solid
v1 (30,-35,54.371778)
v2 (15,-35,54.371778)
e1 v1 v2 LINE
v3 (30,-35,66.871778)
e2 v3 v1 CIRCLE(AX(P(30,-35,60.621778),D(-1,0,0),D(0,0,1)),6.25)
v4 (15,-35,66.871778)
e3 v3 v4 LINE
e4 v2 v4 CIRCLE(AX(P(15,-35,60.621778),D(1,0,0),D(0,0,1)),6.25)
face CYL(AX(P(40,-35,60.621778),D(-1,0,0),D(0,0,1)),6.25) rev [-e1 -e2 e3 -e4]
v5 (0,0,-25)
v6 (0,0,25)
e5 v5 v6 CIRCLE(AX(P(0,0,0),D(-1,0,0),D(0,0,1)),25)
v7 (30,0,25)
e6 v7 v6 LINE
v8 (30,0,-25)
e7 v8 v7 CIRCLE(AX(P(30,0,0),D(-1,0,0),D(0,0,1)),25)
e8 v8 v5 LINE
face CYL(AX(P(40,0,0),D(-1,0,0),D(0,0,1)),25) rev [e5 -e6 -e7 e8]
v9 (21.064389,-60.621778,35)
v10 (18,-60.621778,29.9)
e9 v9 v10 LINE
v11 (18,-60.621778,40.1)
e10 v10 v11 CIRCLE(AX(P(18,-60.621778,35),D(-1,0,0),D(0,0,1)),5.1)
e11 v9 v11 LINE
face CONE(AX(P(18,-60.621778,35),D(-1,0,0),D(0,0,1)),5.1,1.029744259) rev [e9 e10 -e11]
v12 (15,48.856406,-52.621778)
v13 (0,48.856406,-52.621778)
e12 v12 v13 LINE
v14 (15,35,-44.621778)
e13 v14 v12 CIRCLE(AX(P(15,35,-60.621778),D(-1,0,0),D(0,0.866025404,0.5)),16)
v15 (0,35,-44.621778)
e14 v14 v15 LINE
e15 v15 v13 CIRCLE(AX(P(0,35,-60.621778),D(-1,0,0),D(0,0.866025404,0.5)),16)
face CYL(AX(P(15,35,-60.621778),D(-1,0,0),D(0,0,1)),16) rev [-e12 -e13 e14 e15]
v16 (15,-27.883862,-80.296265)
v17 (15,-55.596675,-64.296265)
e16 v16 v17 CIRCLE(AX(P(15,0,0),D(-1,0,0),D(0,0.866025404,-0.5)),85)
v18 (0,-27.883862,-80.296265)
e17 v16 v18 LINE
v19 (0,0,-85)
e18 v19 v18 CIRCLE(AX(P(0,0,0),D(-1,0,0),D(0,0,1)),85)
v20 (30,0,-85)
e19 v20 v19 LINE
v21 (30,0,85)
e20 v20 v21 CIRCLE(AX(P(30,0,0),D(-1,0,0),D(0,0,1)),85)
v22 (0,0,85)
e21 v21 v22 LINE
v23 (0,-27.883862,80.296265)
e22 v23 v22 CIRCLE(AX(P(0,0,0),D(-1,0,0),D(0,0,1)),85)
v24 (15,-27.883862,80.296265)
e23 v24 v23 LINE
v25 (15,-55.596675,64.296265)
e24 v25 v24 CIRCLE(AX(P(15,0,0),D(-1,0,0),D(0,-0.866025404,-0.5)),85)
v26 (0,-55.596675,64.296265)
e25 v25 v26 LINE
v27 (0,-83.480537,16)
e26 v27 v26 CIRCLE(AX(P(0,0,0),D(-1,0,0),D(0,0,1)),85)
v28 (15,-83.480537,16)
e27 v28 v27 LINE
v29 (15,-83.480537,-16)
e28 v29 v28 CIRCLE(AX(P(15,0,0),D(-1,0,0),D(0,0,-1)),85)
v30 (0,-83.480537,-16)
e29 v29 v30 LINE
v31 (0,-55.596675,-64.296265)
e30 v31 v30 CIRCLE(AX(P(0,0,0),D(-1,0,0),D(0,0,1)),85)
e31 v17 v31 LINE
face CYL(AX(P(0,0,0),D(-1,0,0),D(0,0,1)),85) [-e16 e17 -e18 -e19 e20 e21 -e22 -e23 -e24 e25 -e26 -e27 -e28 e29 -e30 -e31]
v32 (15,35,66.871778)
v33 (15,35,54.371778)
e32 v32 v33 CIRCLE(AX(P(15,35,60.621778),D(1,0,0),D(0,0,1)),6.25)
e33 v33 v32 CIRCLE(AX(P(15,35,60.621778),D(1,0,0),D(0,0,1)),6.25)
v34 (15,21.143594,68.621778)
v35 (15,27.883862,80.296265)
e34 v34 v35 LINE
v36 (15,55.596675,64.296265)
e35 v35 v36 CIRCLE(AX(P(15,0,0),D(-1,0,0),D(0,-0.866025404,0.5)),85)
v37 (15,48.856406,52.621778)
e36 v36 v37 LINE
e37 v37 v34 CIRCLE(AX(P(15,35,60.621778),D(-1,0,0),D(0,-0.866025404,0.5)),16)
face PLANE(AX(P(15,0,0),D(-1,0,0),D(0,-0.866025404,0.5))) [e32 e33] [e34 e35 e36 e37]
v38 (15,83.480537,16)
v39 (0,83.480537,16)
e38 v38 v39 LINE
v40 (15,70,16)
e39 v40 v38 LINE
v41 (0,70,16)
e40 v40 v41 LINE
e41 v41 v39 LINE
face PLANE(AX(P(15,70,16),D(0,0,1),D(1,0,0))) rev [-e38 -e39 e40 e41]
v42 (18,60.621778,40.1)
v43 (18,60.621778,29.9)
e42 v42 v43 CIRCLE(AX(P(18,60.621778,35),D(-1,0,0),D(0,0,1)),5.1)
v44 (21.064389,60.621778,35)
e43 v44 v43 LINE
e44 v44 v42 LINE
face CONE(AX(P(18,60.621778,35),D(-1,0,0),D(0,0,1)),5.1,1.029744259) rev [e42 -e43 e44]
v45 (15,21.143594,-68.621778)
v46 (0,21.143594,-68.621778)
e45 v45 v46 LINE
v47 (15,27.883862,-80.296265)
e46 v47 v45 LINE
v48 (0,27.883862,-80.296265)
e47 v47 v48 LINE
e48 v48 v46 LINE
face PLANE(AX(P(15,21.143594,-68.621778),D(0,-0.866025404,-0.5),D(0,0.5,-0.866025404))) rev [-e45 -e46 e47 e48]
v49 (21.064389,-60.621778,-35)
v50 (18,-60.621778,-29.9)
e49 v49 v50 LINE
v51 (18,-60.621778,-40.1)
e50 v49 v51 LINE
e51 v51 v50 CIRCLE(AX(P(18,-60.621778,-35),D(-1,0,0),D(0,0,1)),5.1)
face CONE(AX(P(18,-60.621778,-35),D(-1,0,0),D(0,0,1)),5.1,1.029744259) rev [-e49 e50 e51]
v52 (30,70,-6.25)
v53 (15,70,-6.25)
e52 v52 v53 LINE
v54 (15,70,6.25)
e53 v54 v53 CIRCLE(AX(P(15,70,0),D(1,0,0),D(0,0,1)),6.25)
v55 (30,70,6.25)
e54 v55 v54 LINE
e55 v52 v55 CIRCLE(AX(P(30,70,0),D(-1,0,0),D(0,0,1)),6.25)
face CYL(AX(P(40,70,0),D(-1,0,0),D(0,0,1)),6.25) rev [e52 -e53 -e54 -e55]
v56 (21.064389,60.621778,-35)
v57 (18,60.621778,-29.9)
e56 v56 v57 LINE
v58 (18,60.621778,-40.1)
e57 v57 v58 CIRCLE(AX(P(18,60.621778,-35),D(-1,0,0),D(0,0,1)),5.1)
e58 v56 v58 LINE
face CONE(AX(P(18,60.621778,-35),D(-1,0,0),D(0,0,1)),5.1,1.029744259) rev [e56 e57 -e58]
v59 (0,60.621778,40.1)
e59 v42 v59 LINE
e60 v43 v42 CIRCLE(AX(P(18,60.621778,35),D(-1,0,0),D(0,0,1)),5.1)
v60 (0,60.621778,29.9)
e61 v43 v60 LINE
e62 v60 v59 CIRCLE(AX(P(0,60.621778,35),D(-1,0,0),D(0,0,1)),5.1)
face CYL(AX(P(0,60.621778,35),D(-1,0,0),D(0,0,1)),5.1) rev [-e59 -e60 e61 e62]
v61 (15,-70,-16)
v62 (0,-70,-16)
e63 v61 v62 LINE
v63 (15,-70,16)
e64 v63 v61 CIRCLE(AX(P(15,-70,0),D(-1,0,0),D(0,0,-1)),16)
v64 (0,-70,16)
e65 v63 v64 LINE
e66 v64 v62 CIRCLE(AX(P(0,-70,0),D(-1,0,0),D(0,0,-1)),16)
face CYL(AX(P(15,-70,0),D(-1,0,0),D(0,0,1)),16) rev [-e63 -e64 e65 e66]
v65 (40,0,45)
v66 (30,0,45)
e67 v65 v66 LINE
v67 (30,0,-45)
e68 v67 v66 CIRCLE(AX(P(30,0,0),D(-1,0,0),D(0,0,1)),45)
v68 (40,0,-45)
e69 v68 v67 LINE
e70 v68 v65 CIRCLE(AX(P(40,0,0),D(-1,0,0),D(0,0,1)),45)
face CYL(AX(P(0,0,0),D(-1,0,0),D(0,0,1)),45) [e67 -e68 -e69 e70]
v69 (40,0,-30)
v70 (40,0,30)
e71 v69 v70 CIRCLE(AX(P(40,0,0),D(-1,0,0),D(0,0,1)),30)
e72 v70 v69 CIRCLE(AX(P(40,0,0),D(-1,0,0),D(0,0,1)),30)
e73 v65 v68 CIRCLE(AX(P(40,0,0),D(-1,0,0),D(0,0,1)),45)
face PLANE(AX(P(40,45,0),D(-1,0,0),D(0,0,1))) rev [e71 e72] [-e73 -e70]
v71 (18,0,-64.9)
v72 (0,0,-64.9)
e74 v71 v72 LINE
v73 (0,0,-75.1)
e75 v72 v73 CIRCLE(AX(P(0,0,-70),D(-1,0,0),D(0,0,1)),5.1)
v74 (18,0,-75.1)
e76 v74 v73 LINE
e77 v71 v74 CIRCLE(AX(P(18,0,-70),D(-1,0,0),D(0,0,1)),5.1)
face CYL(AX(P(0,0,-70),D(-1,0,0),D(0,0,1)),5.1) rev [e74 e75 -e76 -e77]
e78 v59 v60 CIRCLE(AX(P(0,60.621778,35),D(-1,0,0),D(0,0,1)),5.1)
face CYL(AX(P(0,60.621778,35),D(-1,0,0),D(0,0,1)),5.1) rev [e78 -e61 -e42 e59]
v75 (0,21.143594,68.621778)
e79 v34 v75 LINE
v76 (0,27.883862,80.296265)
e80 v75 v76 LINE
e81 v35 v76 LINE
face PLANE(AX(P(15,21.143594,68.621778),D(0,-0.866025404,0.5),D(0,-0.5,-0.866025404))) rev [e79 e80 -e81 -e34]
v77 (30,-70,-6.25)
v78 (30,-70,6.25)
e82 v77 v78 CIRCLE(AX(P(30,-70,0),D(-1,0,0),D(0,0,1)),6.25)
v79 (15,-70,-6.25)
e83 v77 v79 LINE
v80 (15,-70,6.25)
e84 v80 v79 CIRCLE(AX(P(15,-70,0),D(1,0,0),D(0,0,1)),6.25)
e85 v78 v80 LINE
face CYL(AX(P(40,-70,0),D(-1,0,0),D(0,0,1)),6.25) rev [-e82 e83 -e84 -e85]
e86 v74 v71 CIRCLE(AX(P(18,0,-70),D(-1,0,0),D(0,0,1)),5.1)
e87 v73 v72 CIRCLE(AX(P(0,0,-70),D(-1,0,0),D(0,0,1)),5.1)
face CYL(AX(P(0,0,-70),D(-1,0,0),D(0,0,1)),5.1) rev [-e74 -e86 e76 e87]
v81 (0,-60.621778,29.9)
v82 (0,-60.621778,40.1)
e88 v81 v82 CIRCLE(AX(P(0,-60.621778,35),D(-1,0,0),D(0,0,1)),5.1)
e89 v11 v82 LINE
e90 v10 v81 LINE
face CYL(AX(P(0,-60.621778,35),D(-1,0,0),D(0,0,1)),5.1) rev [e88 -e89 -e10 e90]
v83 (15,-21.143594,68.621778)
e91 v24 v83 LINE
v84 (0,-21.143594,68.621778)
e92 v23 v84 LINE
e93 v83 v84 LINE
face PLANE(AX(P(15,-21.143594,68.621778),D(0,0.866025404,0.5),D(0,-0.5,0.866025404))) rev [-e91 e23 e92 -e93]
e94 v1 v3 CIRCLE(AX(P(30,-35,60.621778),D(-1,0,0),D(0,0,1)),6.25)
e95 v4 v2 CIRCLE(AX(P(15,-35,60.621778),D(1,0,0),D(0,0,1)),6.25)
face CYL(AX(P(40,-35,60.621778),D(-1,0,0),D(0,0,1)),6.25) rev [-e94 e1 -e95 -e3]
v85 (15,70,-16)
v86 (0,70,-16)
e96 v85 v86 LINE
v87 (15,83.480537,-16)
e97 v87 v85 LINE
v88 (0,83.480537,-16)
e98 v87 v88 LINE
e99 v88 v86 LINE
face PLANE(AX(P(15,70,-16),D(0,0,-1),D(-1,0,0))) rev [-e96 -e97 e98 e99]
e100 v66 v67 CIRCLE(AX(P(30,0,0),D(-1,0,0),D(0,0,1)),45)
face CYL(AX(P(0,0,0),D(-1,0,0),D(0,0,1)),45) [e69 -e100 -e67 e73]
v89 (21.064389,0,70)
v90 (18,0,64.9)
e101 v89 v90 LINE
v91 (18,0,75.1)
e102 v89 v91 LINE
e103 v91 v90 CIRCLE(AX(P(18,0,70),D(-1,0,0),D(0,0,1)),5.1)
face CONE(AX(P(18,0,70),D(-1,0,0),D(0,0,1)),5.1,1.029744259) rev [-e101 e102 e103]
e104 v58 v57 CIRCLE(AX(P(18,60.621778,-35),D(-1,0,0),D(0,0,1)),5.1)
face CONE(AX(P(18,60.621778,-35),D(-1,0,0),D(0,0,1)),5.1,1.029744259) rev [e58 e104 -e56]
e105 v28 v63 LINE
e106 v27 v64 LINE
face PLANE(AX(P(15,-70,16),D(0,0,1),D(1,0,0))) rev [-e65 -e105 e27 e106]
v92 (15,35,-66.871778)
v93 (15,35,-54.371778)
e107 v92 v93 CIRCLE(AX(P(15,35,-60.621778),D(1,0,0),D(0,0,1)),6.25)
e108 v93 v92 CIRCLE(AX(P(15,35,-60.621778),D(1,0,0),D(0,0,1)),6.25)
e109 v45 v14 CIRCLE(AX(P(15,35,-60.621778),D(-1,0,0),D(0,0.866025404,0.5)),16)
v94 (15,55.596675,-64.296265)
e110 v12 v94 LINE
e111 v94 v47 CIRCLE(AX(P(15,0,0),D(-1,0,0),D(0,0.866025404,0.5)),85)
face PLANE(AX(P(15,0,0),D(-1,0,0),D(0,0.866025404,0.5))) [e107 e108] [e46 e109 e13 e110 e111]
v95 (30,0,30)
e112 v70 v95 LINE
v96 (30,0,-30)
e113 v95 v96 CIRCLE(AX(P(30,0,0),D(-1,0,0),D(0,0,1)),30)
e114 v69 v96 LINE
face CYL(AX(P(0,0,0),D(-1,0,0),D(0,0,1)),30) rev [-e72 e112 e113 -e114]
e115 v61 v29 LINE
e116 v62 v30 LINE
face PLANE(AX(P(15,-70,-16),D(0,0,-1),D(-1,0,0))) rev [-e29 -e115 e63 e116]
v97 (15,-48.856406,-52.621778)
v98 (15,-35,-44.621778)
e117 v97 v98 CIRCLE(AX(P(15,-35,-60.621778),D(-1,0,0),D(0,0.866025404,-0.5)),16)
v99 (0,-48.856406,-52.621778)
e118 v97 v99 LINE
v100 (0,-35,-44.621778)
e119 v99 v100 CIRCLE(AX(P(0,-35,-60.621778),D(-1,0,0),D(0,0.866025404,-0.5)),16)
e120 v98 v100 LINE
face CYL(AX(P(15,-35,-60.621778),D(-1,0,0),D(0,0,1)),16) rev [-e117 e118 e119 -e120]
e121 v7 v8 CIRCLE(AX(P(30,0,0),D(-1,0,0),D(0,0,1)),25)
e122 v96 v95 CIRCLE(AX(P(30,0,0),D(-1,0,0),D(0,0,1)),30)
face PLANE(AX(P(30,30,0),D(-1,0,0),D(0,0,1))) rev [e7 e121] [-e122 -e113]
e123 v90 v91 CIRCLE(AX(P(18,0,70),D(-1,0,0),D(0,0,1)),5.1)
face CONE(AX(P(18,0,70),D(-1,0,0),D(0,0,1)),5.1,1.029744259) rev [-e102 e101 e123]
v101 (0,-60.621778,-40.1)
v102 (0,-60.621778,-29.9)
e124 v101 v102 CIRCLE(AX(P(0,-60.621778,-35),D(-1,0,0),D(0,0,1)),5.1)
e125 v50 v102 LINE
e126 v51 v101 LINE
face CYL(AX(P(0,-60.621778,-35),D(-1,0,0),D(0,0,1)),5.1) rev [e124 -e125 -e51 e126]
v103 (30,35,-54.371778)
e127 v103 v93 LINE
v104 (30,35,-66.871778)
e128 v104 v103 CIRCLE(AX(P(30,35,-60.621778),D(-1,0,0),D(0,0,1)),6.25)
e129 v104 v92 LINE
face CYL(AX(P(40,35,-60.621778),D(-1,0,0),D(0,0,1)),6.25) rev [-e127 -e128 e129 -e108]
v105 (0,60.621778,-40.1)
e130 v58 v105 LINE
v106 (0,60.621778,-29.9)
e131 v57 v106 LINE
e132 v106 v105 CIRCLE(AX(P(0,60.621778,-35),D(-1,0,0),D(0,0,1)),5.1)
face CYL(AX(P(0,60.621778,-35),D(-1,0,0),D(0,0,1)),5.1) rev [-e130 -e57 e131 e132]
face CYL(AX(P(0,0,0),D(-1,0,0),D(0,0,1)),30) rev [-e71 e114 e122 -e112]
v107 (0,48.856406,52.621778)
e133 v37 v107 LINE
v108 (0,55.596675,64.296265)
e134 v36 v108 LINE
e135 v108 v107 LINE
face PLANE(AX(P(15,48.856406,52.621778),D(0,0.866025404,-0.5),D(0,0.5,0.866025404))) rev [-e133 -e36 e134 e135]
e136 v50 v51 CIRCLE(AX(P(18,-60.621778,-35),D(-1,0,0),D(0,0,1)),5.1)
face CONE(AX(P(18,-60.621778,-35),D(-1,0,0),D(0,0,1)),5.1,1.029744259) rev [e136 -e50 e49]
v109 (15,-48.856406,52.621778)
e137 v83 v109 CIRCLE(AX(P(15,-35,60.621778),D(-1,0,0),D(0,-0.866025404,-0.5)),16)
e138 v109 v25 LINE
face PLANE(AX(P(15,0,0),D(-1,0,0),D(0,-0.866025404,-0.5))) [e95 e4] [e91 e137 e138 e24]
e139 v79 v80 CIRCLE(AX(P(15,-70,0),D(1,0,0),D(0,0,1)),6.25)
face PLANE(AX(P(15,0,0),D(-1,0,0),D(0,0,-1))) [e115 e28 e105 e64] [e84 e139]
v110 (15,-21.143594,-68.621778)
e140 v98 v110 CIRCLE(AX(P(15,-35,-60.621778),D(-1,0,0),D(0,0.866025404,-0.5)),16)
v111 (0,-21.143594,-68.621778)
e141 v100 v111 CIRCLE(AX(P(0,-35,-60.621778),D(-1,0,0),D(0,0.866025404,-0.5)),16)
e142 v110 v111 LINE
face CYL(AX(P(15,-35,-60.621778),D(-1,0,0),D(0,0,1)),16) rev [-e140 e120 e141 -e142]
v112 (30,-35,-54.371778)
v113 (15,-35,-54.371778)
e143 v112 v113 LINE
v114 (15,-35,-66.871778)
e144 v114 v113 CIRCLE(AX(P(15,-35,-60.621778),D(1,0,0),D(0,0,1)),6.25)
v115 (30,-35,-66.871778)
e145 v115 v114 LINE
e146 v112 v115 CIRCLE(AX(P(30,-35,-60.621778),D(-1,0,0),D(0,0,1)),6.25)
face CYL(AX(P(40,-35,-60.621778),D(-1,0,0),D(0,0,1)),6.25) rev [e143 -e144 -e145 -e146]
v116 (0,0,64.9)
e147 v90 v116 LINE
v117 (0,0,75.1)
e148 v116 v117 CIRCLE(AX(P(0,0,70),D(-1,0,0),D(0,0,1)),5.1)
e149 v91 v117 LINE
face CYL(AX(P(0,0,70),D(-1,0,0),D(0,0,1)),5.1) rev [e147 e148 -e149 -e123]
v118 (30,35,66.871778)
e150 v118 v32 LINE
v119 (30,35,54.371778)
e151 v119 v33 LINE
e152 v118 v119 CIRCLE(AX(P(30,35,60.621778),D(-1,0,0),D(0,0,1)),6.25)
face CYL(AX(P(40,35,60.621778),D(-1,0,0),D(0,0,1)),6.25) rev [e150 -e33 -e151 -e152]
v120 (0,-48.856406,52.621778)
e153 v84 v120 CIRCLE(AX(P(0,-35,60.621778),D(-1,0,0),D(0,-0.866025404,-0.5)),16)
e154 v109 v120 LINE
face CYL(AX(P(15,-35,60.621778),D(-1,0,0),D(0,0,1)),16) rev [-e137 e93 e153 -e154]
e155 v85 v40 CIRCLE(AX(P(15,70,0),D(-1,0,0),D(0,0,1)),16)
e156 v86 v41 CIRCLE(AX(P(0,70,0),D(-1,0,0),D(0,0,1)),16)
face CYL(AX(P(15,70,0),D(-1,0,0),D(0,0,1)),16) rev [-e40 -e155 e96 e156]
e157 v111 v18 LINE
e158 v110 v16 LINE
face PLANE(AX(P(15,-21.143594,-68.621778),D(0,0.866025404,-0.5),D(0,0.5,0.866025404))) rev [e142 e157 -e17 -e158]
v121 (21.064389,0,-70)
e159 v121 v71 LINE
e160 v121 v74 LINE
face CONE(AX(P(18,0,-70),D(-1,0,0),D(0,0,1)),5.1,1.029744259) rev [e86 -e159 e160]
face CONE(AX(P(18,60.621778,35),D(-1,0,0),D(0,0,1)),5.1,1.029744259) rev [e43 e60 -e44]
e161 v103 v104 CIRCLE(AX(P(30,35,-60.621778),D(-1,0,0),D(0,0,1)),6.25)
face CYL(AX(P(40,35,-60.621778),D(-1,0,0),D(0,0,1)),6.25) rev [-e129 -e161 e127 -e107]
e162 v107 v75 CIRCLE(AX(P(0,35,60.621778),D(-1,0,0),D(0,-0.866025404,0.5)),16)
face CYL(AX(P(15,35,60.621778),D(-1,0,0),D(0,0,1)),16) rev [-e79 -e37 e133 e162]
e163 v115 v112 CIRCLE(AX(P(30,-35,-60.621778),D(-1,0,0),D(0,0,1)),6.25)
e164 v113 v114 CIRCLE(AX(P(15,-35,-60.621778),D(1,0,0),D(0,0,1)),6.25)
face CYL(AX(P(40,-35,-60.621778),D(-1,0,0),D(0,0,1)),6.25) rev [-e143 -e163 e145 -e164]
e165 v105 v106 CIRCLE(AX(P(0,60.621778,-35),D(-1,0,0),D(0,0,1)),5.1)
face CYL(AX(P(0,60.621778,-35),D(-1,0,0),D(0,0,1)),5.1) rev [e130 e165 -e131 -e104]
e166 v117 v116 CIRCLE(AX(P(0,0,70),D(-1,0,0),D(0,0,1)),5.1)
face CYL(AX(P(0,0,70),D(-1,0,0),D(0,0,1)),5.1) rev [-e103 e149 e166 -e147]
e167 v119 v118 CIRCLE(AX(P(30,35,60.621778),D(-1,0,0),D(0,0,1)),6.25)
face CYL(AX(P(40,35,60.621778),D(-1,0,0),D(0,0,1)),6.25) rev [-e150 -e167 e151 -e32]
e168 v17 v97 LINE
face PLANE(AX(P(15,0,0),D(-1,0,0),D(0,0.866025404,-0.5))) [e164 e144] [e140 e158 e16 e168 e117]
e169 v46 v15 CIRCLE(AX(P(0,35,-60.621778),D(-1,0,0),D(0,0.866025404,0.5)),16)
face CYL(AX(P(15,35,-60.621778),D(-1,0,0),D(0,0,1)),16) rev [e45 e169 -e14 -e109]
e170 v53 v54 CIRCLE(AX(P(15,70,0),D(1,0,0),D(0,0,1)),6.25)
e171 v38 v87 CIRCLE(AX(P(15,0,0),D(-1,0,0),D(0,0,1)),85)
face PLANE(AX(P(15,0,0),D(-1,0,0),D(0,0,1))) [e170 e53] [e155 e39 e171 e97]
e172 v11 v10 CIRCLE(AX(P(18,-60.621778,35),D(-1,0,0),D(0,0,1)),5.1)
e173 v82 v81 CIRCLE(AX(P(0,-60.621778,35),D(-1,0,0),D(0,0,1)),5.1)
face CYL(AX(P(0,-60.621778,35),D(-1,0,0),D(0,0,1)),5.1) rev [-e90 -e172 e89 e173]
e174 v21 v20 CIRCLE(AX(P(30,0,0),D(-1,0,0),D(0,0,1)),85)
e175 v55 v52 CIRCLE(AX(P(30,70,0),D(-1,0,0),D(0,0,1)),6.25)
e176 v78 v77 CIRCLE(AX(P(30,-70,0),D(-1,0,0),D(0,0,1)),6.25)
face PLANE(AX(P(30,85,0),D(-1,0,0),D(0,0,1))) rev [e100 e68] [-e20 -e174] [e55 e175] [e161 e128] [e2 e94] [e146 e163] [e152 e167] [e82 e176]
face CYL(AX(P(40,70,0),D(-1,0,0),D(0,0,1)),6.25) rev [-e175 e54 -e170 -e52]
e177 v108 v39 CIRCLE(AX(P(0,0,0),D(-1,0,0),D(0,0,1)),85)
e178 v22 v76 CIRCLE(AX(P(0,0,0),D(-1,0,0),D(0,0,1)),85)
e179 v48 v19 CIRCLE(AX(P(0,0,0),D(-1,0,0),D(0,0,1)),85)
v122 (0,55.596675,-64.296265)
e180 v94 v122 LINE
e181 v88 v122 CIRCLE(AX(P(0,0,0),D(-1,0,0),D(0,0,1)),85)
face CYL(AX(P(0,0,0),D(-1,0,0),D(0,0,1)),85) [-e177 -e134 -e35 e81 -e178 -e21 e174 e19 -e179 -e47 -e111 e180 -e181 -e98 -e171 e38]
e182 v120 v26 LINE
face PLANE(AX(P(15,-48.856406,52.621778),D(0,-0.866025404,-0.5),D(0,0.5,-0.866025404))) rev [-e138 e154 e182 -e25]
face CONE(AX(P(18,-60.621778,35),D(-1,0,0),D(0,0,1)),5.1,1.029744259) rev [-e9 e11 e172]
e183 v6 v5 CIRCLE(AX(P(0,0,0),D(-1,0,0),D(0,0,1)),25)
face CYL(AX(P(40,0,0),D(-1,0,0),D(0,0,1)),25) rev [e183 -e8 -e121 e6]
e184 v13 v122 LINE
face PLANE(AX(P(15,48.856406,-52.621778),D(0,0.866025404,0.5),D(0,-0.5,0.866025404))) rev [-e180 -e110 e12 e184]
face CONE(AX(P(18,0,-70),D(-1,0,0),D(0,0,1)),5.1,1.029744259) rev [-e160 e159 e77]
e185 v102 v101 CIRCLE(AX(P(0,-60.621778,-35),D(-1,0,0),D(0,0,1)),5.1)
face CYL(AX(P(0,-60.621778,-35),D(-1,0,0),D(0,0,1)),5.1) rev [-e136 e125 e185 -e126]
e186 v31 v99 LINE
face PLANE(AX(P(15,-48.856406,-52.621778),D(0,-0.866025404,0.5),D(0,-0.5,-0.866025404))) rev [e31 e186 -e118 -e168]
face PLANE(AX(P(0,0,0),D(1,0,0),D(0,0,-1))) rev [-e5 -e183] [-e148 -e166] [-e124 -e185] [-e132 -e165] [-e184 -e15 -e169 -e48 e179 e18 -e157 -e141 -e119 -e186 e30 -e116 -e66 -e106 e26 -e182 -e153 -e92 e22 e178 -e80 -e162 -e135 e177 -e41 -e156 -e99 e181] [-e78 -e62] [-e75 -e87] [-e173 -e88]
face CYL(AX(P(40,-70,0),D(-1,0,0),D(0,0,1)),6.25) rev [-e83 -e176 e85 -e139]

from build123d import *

# Parameters (mm, degrees)
SKETCH_2_R               = 6.25
CUT_EXTRUDE_1_DEPTH      = 127.688594593
PATTERN_CIRCULAR_1_COUNT = 6
SKETCH_3_R               = 25
CUT_EXTRUDE_2_DEPTH      = 127.688594593
CUT_EXTRUDE_START        = -15
CUT_EXTRUDE_3_DEPTH      = 15
PATTERN_CIRCULAR_2_COUNT = 6
PATTERN_CIRCULAR_3_COUNT = 6


with BuildPart() as part:
    # 草图1 → 旋转1 (revolve)
    with BuildSketch(Plane.XY, mode=Mode.PRIVATE) as revolve_1_sk:
        Polygon((0, 0), (0, 85), (30, 85), (30, 45), (40, 45), (40, 30), (30, 30), (30, 0), align=None)
    revolve(revolve_1_sk.sketch.rotate(Axis((0, 0, 0), (1, 0, 0)), 90), axis=Axis((0, 0, 0), (1, 0, 0)))

    # 草图2 → 切除-拉伸1 (cut, through all)
    with BuildSketch(Plane.ZY):
        with Locations((0, 70)):
            Circle(SKETCH_2_R)
    cut_extrude_1 = extrude(amount=-CUT_EXTRUDE_1_DEPTH, mode=Mode.SUBTRACT)

    # 阵列(圆周)1: 切除-拉伸1 ×6 about axis
    pattern_circular_1_axis = Axis((0, 0, 0), (1, 0, 0))
    for i in range(1, PATTERN_CIRCULAR_1_COUNT):
        add(cut_extrude_1.rotate(pattern_circular_1_axis, i * 360 / PATTERN_CIRCULAR_1_COUNT), mode=Mode.SUBTRACT)

    # 草图3 → 切除-拉伸2 (cut, through all)
    with BuildSketch(Plane.ZY):
        Circle(SKETCH_3_R)
    extrude(amount=-CUT_EXTRUDE_2_DEPTH, mode=Mode.SUBTRACT)

    # 草图6 → 切除-拉伸3 (cut)
    with BuildSketch(Plane.ZY.offset(CUT_EXTRUDE_START)):
        with BuildLine():
            Line((-16, 70), (-16, 83.480536654))
            ThreePointArc((-16, 83.480536654), (0, 85), (16, 83.480536654))
            Line((16, 83.480536654), (16, 70))
            ThreePointArc((16, 70), (0, 54), (-16, 70))
        make_face()
    cut_extrude_3 = extrude(amount=CUT_EXTRUDE_3_DEPTH, mode=Mode.SUBTRACT)

    # 阵列(圆周)2: 切除-拉伸3 ×6 about axis
    pattern_circular_2_axis = Axis((0, 0, 0), (1, 0, 0))
    for i in range(1, PATTERN_CIRCULAR_2_COUNT):
        add(cut_extrude_3.rotate(pattern_circular_2_axis, i * 360 / PATTERN_CIRCULAR_2_COUNT), mode=Mode.SUBTRACT)

    # 草图8 → M12 螺纹孔1 (revolve, cut)
    with BuildSketch(Plane(origin=(0, 60.621778265, 35), x_dir=(0, 0, 1), z_dir=(0, 1, 0))):
        Polygon((0, 0), (0, 21.064389157), (5.1, 18), (5.1, 0), align=None)
    hole_wizard_m12_1 = revolve(axis=Axis((-6.35, 60.621778265, 35), (1, 0, 0)), mode=Mode.SUBTRACT)

    # 阵列(圆周)3: M12 螺纹孔1 ×6 about axis
    pattern_circular_3_axis = Axis((0, 0, 0), (1, 0, 0))
    for i in range(1, PATTERN_CIRCULAR_3_COUNT):
        add(hole_wizard_m12_1.rotate(pattern_circular_3_axis, i * 360 / PATTERN_CIRCULAR_3_COUNT), mode=Mode.SUBTRACT)


solid = part.part
